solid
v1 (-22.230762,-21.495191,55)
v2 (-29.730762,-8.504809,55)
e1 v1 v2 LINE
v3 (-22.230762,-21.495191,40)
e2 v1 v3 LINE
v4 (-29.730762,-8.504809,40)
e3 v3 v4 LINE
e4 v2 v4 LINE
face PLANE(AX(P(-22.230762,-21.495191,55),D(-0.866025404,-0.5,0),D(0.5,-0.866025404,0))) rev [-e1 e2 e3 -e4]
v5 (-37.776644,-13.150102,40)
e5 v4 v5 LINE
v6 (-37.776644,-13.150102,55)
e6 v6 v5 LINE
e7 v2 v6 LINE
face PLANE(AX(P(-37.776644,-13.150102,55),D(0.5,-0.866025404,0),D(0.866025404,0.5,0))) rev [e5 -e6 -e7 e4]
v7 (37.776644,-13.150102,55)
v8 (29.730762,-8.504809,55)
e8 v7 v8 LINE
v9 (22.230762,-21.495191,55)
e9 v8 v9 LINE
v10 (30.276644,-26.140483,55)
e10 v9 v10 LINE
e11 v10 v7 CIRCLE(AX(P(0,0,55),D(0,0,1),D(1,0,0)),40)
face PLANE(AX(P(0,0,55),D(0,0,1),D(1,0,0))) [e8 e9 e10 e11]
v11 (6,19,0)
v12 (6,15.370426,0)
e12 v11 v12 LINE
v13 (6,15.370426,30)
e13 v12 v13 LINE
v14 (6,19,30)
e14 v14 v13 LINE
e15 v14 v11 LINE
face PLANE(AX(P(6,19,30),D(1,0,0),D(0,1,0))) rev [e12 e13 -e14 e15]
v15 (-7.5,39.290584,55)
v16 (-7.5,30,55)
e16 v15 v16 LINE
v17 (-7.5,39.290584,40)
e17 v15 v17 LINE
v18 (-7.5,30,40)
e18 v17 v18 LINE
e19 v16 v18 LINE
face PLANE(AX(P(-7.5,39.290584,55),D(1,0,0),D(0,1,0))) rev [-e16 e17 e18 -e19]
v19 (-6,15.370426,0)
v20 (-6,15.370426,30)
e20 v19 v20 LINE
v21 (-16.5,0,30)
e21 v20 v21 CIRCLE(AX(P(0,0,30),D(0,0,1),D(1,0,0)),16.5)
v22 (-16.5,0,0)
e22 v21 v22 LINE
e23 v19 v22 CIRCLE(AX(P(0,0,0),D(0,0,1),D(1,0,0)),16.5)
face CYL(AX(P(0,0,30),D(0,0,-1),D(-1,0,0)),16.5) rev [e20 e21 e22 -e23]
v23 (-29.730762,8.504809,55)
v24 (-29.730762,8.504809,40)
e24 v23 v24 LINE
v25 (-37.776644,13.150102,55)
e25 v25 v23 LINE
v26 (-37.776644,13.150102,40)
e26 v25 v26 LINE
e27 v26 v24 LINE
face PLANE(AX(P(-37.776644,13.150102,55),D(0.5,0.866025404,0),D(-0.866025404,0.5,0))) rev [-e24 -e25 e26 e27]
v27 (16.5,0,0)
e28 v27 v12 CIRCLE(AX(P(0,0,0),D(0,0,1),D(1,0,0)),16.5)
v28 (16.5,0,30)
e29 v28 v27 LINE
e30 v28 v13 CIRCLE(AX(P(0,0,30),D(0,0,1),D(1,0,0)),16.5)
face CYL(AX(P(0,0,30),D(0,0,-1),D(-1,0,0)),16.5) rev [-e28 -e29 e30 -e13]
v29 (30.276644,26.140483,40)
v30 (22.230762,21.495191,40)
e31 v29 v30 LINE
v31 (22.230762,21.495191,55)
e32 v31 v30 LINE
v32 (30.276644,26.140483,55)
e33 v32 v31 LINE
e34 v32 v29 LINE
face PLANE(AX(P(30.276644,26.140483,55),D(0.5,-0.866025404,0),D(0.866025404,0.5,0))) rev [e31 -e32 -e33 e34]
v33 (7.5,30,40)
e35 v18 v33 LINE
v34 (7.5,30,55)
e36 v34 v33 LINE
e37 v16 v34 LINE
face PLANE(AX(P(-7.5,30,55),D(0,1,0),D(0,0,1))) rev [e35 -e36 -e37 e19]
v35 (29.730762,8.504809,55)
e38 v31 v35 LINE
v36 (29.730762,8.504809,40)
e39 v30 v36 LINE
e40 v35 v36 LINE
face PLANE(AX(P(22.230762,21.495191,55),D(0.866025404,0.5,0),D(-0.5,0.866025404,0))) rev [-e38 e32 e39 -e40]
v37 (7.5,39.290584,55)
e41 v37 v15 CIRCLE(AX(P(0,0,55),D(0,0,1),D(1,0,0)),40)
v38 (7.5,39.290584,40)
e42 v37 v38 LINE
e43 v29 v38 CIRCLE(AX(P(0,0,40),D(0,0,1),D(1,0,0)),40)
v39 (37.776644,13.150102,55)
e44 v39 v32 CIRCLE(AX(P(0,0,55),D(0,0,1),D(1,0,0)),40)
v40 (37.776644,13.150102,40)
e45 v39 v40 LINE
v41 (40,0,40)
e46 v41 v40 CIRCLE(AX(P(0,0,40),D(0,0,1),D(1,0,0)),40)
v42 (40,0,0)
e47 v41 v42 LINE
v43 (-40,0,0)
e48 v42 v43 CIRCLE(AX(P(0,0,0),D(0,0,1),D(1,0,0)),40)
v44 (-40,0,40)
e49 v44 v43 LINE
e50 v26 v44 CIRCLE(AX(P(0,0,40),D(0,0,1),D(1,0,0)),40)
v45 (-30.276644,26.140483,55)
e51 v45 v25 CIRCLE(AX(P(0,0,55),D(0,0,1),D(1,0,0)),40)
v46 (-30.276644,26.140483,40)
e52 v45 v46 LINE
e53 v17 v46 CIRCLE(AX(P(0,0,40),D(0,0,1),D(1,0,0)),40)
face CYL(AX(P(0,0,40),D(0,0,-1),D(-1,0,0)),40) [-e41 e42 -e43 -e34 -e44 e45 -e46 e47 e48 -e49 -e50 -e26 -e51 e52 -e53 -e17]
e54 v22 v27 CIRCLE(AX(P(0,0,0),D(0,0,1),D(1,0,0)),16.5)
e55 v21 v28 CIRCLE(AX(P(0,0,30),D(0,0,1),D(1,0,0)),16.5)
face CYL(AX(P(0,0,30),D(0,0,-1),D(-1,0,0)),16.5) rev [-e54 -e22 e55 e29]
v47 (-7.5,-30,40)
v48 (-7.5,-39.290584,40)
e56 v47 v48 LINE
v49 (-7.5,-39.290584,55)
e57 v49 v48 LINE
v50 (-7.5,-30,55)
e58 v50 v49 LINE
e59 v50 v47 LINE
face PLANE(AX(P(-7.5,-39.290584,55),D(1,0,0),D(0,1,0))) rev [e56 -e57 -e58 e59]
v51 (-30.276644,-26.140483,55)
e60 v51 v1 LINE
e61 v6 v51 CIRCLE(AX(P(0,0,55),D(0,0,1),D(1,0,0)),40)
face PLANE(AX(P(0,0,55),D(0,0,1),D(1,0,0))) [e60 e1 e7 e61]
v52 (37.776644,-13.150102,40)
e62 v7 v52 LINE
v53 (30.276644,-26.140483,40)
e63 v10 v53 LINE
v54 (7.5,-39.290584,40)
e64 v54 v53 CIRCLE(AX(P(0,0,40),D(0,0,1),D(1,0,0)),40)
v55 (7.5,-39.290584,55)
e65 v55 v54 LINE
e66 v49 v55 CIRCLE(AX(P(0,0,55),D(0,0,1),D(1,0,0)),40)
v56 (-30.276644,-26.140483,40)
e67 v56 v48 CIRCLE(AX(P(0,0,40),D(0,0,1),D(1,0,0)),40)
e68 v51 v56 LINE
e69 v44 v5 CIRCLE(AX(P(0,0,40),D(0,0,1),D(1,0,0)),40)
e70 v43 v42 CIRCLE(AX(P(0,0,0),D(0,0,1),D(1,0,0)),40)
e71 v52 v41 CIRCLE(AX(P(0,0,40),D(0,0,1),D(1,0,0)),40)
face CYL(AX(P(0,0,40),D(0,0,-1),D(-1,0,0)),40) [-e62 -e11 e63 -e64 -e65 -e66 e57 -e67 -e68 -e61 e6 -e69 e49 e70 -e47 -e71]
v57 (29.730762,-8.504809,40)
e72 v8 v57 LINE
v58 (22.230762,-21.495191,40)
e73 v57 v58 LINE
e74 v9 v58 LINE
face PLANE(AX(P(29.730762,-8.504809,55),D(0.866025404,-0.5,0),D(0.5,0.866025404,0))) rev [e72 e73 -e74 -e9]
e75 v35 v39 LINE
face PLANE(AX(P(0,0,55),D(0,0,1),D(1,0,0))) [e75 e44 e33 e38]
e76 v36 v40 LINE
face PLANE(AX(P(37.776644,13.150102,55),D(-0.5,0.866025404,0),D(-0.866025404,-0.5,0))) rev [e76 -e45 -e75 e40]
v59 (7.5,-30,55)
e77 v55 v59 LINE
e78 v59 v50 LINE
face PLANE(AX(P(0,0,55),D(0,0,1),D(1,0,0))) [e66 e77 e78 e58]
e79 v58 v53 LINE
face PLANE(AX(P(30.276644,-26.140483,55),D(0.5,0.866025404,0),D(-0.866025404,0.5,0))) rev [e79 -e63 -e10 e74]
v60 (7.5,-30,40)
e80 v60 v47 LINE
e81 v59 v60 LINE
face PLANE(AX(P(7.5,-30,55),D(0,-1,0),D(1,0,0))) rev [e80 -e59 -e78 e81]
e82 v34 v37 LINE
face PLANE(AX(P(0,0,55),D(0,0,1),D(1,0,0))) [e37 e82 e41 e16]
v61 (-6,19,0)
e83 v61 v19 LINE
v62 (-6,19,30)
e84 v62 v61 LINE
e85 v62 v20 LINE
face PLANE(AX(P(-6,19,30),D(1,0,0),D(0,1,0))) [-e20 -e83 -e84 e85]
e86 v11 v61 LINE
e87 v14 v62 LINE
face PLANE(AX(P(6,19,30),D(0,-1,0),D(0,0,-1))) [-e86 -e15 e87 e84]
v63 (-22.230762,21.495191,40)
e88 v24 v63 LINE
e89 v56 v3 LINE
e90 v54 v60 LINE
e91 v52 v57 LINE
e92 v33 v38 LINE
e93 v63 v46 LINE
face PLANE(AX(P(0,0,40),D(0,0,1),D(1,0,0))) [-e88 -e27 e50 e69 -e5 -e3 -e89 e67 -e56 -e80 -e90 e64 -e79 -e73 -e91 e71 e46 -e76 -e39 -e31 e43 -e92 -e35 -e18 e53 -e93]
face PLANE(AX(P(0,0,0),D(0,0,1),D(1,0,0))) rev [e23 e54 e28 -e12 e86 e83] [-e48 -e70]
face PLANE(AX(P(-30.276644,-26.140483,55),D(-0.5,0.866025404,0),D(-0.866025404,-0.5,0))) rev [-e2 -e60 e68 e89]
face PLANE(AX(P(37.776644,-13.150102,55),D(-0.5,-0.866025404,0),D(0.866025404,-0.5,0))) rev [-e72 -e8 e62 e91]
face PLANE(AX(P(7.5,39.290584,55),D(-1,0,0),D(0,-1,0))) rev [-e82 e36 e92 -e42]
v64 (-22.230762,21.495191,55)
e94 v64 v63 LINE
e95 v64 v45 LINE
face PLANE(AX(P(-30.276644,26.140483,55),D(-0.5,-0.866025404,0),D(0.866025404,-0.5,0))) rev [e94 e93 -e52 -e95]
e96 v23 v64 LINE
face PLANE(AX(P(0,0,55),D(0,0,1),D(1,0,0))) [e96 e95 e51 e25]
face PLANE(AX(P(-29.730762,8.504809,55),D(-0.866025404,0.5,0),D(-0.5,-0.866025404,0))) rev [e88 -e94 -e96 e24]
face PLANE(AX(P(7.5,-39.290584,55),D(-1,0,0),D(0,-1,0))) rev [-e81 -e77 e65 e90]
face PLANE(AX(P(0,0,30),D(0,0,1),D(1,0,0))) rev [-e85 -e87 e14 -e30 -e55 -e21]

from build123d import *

# Parameters (mm, degrees)
SKETCH_2_R          = 40
EXTRUDE_1_DEPTH     = 40
SKETCH_1_R          = 16.5
CUT_EXTRUDE_1_DEPTH = 30
EXTRUDE_2_DEPTH     = 15
SKETCH_4_W          = 12
SKETCH_4_H          = 7.528633981
CUT_EXTRUDE_2_DEPTH = 30


with BuildPart() as part:
    # 草图2 → 凸台-拉伸1 (new body)
    with BuildSketch(Plane.XY):
        Circle(SKETCH_2_R)
    extrude(amount=EXTRUDE_1_DEPTH)

    # 草图1 → 切除-拉伸1 (cut)
    with BuildSketch(Plane.XY):
        Circle(SKETCH_1_R)
    extrude(amount=CUT_EXTRUDE_1_DEPTH, mode=Mode.SUBTRACT)

    # 草图3 → 凸台-拉伸2 (add)
    with BuildSketch(Plane.XY.offset(40)):
        with BuildLine():
            Line((22.230762114, 21.495190528), (29.730762114, 8.504809472))
            Line((29.730762114, 8.504809472), (37.776643972, 13.150101528))
            ThreePointArc((37.776643972, 13.150101528), (34.641016151, 20), (30.276643972, 26.140482585))
            Line((30.276643972, 26.140482585), (22.230762114, 21.495190528))
        make_face()
        with BuildLine():
            Line((-7.5, 39.290584114), (-7.5, 30))
            Line((-7.5, 30), (7.5, 30))
            Line((7.5, 30), (7.5, 39.290584114))
            ThreePointArc((7.5, 39.290584114), (0, 40), (-7.5, 39.290584114))
        make_face()
        with BuildLine():
            Line((29.730762114, -8.504809472), (22.230762114, -21.495190528))
            Line((22.230762114, -21.495190528), (30.276643972, -26.140482585))
            ThreePointArc((30.276643972, -26.140482585), (34.641016151, -20), (37.776643972, -13.150101528))
            Line((37.776643972, -13.150101528), (29.730762114, -8.504809472))
        make_face()
        with BuildLine():
            Line((7.5, -30), (-7.5, -30))
            Line((-7.5, -30), (-7.5, -39.290584114))
            ThreePointArc((-7.5, -39.290584114), (0, -40), (7.5, -39.290584114))
            Line((7.5, -39.290584114), (7.5, -30))
        make_face()
        with BuildLine():
            Line((-22.230762114, -21.495190528), (-29.730762114, -8.504809472))
            Line((-29.730762114, -8.504809472), (-37.776643972, -13.150101528))
            ThreePointArc((-37.776643972, -13.150101528), (-34.641016151, -20), (-30.276643972, -26.140482585))
            Line((-30.276643972, -26.140482585), (-22.230762114, -21.495190528))
        make_face()
        with BuildLine():
            Line((-29.730762114, 8.504809472), (-22.230762114, 21.495190528))
            Line((-22.230762114, 21.495190528), (-30.276643972, 26.140482585))
            ThreePointArc((-30.276643972, 26.140482585), (-34.641016151, 20), (-37.776643972, 13.150101528))
            Line((-37.776643972, 13.150101528), (-29.730762114, 8.504809472))
        make_face()
    extrude(amount=EXTRUDE_2_DEPTH)

    # 草图4 → 切除-拉伸2 (cut)
    with BuildSketch(Plane(origin=(0, 0, 0), x_dir=(-1, 0, 0), z_dir=(0, 0, -1))):
        with Locations((0, 15.23568301)):
            Rectangle(SKETCH_4_W, SKETCH_4_H)
    extrude(amount=-CUT_EXTRUDE_2_DEPTH, mode=Mode.SUBTRACT)


solid = part.part
